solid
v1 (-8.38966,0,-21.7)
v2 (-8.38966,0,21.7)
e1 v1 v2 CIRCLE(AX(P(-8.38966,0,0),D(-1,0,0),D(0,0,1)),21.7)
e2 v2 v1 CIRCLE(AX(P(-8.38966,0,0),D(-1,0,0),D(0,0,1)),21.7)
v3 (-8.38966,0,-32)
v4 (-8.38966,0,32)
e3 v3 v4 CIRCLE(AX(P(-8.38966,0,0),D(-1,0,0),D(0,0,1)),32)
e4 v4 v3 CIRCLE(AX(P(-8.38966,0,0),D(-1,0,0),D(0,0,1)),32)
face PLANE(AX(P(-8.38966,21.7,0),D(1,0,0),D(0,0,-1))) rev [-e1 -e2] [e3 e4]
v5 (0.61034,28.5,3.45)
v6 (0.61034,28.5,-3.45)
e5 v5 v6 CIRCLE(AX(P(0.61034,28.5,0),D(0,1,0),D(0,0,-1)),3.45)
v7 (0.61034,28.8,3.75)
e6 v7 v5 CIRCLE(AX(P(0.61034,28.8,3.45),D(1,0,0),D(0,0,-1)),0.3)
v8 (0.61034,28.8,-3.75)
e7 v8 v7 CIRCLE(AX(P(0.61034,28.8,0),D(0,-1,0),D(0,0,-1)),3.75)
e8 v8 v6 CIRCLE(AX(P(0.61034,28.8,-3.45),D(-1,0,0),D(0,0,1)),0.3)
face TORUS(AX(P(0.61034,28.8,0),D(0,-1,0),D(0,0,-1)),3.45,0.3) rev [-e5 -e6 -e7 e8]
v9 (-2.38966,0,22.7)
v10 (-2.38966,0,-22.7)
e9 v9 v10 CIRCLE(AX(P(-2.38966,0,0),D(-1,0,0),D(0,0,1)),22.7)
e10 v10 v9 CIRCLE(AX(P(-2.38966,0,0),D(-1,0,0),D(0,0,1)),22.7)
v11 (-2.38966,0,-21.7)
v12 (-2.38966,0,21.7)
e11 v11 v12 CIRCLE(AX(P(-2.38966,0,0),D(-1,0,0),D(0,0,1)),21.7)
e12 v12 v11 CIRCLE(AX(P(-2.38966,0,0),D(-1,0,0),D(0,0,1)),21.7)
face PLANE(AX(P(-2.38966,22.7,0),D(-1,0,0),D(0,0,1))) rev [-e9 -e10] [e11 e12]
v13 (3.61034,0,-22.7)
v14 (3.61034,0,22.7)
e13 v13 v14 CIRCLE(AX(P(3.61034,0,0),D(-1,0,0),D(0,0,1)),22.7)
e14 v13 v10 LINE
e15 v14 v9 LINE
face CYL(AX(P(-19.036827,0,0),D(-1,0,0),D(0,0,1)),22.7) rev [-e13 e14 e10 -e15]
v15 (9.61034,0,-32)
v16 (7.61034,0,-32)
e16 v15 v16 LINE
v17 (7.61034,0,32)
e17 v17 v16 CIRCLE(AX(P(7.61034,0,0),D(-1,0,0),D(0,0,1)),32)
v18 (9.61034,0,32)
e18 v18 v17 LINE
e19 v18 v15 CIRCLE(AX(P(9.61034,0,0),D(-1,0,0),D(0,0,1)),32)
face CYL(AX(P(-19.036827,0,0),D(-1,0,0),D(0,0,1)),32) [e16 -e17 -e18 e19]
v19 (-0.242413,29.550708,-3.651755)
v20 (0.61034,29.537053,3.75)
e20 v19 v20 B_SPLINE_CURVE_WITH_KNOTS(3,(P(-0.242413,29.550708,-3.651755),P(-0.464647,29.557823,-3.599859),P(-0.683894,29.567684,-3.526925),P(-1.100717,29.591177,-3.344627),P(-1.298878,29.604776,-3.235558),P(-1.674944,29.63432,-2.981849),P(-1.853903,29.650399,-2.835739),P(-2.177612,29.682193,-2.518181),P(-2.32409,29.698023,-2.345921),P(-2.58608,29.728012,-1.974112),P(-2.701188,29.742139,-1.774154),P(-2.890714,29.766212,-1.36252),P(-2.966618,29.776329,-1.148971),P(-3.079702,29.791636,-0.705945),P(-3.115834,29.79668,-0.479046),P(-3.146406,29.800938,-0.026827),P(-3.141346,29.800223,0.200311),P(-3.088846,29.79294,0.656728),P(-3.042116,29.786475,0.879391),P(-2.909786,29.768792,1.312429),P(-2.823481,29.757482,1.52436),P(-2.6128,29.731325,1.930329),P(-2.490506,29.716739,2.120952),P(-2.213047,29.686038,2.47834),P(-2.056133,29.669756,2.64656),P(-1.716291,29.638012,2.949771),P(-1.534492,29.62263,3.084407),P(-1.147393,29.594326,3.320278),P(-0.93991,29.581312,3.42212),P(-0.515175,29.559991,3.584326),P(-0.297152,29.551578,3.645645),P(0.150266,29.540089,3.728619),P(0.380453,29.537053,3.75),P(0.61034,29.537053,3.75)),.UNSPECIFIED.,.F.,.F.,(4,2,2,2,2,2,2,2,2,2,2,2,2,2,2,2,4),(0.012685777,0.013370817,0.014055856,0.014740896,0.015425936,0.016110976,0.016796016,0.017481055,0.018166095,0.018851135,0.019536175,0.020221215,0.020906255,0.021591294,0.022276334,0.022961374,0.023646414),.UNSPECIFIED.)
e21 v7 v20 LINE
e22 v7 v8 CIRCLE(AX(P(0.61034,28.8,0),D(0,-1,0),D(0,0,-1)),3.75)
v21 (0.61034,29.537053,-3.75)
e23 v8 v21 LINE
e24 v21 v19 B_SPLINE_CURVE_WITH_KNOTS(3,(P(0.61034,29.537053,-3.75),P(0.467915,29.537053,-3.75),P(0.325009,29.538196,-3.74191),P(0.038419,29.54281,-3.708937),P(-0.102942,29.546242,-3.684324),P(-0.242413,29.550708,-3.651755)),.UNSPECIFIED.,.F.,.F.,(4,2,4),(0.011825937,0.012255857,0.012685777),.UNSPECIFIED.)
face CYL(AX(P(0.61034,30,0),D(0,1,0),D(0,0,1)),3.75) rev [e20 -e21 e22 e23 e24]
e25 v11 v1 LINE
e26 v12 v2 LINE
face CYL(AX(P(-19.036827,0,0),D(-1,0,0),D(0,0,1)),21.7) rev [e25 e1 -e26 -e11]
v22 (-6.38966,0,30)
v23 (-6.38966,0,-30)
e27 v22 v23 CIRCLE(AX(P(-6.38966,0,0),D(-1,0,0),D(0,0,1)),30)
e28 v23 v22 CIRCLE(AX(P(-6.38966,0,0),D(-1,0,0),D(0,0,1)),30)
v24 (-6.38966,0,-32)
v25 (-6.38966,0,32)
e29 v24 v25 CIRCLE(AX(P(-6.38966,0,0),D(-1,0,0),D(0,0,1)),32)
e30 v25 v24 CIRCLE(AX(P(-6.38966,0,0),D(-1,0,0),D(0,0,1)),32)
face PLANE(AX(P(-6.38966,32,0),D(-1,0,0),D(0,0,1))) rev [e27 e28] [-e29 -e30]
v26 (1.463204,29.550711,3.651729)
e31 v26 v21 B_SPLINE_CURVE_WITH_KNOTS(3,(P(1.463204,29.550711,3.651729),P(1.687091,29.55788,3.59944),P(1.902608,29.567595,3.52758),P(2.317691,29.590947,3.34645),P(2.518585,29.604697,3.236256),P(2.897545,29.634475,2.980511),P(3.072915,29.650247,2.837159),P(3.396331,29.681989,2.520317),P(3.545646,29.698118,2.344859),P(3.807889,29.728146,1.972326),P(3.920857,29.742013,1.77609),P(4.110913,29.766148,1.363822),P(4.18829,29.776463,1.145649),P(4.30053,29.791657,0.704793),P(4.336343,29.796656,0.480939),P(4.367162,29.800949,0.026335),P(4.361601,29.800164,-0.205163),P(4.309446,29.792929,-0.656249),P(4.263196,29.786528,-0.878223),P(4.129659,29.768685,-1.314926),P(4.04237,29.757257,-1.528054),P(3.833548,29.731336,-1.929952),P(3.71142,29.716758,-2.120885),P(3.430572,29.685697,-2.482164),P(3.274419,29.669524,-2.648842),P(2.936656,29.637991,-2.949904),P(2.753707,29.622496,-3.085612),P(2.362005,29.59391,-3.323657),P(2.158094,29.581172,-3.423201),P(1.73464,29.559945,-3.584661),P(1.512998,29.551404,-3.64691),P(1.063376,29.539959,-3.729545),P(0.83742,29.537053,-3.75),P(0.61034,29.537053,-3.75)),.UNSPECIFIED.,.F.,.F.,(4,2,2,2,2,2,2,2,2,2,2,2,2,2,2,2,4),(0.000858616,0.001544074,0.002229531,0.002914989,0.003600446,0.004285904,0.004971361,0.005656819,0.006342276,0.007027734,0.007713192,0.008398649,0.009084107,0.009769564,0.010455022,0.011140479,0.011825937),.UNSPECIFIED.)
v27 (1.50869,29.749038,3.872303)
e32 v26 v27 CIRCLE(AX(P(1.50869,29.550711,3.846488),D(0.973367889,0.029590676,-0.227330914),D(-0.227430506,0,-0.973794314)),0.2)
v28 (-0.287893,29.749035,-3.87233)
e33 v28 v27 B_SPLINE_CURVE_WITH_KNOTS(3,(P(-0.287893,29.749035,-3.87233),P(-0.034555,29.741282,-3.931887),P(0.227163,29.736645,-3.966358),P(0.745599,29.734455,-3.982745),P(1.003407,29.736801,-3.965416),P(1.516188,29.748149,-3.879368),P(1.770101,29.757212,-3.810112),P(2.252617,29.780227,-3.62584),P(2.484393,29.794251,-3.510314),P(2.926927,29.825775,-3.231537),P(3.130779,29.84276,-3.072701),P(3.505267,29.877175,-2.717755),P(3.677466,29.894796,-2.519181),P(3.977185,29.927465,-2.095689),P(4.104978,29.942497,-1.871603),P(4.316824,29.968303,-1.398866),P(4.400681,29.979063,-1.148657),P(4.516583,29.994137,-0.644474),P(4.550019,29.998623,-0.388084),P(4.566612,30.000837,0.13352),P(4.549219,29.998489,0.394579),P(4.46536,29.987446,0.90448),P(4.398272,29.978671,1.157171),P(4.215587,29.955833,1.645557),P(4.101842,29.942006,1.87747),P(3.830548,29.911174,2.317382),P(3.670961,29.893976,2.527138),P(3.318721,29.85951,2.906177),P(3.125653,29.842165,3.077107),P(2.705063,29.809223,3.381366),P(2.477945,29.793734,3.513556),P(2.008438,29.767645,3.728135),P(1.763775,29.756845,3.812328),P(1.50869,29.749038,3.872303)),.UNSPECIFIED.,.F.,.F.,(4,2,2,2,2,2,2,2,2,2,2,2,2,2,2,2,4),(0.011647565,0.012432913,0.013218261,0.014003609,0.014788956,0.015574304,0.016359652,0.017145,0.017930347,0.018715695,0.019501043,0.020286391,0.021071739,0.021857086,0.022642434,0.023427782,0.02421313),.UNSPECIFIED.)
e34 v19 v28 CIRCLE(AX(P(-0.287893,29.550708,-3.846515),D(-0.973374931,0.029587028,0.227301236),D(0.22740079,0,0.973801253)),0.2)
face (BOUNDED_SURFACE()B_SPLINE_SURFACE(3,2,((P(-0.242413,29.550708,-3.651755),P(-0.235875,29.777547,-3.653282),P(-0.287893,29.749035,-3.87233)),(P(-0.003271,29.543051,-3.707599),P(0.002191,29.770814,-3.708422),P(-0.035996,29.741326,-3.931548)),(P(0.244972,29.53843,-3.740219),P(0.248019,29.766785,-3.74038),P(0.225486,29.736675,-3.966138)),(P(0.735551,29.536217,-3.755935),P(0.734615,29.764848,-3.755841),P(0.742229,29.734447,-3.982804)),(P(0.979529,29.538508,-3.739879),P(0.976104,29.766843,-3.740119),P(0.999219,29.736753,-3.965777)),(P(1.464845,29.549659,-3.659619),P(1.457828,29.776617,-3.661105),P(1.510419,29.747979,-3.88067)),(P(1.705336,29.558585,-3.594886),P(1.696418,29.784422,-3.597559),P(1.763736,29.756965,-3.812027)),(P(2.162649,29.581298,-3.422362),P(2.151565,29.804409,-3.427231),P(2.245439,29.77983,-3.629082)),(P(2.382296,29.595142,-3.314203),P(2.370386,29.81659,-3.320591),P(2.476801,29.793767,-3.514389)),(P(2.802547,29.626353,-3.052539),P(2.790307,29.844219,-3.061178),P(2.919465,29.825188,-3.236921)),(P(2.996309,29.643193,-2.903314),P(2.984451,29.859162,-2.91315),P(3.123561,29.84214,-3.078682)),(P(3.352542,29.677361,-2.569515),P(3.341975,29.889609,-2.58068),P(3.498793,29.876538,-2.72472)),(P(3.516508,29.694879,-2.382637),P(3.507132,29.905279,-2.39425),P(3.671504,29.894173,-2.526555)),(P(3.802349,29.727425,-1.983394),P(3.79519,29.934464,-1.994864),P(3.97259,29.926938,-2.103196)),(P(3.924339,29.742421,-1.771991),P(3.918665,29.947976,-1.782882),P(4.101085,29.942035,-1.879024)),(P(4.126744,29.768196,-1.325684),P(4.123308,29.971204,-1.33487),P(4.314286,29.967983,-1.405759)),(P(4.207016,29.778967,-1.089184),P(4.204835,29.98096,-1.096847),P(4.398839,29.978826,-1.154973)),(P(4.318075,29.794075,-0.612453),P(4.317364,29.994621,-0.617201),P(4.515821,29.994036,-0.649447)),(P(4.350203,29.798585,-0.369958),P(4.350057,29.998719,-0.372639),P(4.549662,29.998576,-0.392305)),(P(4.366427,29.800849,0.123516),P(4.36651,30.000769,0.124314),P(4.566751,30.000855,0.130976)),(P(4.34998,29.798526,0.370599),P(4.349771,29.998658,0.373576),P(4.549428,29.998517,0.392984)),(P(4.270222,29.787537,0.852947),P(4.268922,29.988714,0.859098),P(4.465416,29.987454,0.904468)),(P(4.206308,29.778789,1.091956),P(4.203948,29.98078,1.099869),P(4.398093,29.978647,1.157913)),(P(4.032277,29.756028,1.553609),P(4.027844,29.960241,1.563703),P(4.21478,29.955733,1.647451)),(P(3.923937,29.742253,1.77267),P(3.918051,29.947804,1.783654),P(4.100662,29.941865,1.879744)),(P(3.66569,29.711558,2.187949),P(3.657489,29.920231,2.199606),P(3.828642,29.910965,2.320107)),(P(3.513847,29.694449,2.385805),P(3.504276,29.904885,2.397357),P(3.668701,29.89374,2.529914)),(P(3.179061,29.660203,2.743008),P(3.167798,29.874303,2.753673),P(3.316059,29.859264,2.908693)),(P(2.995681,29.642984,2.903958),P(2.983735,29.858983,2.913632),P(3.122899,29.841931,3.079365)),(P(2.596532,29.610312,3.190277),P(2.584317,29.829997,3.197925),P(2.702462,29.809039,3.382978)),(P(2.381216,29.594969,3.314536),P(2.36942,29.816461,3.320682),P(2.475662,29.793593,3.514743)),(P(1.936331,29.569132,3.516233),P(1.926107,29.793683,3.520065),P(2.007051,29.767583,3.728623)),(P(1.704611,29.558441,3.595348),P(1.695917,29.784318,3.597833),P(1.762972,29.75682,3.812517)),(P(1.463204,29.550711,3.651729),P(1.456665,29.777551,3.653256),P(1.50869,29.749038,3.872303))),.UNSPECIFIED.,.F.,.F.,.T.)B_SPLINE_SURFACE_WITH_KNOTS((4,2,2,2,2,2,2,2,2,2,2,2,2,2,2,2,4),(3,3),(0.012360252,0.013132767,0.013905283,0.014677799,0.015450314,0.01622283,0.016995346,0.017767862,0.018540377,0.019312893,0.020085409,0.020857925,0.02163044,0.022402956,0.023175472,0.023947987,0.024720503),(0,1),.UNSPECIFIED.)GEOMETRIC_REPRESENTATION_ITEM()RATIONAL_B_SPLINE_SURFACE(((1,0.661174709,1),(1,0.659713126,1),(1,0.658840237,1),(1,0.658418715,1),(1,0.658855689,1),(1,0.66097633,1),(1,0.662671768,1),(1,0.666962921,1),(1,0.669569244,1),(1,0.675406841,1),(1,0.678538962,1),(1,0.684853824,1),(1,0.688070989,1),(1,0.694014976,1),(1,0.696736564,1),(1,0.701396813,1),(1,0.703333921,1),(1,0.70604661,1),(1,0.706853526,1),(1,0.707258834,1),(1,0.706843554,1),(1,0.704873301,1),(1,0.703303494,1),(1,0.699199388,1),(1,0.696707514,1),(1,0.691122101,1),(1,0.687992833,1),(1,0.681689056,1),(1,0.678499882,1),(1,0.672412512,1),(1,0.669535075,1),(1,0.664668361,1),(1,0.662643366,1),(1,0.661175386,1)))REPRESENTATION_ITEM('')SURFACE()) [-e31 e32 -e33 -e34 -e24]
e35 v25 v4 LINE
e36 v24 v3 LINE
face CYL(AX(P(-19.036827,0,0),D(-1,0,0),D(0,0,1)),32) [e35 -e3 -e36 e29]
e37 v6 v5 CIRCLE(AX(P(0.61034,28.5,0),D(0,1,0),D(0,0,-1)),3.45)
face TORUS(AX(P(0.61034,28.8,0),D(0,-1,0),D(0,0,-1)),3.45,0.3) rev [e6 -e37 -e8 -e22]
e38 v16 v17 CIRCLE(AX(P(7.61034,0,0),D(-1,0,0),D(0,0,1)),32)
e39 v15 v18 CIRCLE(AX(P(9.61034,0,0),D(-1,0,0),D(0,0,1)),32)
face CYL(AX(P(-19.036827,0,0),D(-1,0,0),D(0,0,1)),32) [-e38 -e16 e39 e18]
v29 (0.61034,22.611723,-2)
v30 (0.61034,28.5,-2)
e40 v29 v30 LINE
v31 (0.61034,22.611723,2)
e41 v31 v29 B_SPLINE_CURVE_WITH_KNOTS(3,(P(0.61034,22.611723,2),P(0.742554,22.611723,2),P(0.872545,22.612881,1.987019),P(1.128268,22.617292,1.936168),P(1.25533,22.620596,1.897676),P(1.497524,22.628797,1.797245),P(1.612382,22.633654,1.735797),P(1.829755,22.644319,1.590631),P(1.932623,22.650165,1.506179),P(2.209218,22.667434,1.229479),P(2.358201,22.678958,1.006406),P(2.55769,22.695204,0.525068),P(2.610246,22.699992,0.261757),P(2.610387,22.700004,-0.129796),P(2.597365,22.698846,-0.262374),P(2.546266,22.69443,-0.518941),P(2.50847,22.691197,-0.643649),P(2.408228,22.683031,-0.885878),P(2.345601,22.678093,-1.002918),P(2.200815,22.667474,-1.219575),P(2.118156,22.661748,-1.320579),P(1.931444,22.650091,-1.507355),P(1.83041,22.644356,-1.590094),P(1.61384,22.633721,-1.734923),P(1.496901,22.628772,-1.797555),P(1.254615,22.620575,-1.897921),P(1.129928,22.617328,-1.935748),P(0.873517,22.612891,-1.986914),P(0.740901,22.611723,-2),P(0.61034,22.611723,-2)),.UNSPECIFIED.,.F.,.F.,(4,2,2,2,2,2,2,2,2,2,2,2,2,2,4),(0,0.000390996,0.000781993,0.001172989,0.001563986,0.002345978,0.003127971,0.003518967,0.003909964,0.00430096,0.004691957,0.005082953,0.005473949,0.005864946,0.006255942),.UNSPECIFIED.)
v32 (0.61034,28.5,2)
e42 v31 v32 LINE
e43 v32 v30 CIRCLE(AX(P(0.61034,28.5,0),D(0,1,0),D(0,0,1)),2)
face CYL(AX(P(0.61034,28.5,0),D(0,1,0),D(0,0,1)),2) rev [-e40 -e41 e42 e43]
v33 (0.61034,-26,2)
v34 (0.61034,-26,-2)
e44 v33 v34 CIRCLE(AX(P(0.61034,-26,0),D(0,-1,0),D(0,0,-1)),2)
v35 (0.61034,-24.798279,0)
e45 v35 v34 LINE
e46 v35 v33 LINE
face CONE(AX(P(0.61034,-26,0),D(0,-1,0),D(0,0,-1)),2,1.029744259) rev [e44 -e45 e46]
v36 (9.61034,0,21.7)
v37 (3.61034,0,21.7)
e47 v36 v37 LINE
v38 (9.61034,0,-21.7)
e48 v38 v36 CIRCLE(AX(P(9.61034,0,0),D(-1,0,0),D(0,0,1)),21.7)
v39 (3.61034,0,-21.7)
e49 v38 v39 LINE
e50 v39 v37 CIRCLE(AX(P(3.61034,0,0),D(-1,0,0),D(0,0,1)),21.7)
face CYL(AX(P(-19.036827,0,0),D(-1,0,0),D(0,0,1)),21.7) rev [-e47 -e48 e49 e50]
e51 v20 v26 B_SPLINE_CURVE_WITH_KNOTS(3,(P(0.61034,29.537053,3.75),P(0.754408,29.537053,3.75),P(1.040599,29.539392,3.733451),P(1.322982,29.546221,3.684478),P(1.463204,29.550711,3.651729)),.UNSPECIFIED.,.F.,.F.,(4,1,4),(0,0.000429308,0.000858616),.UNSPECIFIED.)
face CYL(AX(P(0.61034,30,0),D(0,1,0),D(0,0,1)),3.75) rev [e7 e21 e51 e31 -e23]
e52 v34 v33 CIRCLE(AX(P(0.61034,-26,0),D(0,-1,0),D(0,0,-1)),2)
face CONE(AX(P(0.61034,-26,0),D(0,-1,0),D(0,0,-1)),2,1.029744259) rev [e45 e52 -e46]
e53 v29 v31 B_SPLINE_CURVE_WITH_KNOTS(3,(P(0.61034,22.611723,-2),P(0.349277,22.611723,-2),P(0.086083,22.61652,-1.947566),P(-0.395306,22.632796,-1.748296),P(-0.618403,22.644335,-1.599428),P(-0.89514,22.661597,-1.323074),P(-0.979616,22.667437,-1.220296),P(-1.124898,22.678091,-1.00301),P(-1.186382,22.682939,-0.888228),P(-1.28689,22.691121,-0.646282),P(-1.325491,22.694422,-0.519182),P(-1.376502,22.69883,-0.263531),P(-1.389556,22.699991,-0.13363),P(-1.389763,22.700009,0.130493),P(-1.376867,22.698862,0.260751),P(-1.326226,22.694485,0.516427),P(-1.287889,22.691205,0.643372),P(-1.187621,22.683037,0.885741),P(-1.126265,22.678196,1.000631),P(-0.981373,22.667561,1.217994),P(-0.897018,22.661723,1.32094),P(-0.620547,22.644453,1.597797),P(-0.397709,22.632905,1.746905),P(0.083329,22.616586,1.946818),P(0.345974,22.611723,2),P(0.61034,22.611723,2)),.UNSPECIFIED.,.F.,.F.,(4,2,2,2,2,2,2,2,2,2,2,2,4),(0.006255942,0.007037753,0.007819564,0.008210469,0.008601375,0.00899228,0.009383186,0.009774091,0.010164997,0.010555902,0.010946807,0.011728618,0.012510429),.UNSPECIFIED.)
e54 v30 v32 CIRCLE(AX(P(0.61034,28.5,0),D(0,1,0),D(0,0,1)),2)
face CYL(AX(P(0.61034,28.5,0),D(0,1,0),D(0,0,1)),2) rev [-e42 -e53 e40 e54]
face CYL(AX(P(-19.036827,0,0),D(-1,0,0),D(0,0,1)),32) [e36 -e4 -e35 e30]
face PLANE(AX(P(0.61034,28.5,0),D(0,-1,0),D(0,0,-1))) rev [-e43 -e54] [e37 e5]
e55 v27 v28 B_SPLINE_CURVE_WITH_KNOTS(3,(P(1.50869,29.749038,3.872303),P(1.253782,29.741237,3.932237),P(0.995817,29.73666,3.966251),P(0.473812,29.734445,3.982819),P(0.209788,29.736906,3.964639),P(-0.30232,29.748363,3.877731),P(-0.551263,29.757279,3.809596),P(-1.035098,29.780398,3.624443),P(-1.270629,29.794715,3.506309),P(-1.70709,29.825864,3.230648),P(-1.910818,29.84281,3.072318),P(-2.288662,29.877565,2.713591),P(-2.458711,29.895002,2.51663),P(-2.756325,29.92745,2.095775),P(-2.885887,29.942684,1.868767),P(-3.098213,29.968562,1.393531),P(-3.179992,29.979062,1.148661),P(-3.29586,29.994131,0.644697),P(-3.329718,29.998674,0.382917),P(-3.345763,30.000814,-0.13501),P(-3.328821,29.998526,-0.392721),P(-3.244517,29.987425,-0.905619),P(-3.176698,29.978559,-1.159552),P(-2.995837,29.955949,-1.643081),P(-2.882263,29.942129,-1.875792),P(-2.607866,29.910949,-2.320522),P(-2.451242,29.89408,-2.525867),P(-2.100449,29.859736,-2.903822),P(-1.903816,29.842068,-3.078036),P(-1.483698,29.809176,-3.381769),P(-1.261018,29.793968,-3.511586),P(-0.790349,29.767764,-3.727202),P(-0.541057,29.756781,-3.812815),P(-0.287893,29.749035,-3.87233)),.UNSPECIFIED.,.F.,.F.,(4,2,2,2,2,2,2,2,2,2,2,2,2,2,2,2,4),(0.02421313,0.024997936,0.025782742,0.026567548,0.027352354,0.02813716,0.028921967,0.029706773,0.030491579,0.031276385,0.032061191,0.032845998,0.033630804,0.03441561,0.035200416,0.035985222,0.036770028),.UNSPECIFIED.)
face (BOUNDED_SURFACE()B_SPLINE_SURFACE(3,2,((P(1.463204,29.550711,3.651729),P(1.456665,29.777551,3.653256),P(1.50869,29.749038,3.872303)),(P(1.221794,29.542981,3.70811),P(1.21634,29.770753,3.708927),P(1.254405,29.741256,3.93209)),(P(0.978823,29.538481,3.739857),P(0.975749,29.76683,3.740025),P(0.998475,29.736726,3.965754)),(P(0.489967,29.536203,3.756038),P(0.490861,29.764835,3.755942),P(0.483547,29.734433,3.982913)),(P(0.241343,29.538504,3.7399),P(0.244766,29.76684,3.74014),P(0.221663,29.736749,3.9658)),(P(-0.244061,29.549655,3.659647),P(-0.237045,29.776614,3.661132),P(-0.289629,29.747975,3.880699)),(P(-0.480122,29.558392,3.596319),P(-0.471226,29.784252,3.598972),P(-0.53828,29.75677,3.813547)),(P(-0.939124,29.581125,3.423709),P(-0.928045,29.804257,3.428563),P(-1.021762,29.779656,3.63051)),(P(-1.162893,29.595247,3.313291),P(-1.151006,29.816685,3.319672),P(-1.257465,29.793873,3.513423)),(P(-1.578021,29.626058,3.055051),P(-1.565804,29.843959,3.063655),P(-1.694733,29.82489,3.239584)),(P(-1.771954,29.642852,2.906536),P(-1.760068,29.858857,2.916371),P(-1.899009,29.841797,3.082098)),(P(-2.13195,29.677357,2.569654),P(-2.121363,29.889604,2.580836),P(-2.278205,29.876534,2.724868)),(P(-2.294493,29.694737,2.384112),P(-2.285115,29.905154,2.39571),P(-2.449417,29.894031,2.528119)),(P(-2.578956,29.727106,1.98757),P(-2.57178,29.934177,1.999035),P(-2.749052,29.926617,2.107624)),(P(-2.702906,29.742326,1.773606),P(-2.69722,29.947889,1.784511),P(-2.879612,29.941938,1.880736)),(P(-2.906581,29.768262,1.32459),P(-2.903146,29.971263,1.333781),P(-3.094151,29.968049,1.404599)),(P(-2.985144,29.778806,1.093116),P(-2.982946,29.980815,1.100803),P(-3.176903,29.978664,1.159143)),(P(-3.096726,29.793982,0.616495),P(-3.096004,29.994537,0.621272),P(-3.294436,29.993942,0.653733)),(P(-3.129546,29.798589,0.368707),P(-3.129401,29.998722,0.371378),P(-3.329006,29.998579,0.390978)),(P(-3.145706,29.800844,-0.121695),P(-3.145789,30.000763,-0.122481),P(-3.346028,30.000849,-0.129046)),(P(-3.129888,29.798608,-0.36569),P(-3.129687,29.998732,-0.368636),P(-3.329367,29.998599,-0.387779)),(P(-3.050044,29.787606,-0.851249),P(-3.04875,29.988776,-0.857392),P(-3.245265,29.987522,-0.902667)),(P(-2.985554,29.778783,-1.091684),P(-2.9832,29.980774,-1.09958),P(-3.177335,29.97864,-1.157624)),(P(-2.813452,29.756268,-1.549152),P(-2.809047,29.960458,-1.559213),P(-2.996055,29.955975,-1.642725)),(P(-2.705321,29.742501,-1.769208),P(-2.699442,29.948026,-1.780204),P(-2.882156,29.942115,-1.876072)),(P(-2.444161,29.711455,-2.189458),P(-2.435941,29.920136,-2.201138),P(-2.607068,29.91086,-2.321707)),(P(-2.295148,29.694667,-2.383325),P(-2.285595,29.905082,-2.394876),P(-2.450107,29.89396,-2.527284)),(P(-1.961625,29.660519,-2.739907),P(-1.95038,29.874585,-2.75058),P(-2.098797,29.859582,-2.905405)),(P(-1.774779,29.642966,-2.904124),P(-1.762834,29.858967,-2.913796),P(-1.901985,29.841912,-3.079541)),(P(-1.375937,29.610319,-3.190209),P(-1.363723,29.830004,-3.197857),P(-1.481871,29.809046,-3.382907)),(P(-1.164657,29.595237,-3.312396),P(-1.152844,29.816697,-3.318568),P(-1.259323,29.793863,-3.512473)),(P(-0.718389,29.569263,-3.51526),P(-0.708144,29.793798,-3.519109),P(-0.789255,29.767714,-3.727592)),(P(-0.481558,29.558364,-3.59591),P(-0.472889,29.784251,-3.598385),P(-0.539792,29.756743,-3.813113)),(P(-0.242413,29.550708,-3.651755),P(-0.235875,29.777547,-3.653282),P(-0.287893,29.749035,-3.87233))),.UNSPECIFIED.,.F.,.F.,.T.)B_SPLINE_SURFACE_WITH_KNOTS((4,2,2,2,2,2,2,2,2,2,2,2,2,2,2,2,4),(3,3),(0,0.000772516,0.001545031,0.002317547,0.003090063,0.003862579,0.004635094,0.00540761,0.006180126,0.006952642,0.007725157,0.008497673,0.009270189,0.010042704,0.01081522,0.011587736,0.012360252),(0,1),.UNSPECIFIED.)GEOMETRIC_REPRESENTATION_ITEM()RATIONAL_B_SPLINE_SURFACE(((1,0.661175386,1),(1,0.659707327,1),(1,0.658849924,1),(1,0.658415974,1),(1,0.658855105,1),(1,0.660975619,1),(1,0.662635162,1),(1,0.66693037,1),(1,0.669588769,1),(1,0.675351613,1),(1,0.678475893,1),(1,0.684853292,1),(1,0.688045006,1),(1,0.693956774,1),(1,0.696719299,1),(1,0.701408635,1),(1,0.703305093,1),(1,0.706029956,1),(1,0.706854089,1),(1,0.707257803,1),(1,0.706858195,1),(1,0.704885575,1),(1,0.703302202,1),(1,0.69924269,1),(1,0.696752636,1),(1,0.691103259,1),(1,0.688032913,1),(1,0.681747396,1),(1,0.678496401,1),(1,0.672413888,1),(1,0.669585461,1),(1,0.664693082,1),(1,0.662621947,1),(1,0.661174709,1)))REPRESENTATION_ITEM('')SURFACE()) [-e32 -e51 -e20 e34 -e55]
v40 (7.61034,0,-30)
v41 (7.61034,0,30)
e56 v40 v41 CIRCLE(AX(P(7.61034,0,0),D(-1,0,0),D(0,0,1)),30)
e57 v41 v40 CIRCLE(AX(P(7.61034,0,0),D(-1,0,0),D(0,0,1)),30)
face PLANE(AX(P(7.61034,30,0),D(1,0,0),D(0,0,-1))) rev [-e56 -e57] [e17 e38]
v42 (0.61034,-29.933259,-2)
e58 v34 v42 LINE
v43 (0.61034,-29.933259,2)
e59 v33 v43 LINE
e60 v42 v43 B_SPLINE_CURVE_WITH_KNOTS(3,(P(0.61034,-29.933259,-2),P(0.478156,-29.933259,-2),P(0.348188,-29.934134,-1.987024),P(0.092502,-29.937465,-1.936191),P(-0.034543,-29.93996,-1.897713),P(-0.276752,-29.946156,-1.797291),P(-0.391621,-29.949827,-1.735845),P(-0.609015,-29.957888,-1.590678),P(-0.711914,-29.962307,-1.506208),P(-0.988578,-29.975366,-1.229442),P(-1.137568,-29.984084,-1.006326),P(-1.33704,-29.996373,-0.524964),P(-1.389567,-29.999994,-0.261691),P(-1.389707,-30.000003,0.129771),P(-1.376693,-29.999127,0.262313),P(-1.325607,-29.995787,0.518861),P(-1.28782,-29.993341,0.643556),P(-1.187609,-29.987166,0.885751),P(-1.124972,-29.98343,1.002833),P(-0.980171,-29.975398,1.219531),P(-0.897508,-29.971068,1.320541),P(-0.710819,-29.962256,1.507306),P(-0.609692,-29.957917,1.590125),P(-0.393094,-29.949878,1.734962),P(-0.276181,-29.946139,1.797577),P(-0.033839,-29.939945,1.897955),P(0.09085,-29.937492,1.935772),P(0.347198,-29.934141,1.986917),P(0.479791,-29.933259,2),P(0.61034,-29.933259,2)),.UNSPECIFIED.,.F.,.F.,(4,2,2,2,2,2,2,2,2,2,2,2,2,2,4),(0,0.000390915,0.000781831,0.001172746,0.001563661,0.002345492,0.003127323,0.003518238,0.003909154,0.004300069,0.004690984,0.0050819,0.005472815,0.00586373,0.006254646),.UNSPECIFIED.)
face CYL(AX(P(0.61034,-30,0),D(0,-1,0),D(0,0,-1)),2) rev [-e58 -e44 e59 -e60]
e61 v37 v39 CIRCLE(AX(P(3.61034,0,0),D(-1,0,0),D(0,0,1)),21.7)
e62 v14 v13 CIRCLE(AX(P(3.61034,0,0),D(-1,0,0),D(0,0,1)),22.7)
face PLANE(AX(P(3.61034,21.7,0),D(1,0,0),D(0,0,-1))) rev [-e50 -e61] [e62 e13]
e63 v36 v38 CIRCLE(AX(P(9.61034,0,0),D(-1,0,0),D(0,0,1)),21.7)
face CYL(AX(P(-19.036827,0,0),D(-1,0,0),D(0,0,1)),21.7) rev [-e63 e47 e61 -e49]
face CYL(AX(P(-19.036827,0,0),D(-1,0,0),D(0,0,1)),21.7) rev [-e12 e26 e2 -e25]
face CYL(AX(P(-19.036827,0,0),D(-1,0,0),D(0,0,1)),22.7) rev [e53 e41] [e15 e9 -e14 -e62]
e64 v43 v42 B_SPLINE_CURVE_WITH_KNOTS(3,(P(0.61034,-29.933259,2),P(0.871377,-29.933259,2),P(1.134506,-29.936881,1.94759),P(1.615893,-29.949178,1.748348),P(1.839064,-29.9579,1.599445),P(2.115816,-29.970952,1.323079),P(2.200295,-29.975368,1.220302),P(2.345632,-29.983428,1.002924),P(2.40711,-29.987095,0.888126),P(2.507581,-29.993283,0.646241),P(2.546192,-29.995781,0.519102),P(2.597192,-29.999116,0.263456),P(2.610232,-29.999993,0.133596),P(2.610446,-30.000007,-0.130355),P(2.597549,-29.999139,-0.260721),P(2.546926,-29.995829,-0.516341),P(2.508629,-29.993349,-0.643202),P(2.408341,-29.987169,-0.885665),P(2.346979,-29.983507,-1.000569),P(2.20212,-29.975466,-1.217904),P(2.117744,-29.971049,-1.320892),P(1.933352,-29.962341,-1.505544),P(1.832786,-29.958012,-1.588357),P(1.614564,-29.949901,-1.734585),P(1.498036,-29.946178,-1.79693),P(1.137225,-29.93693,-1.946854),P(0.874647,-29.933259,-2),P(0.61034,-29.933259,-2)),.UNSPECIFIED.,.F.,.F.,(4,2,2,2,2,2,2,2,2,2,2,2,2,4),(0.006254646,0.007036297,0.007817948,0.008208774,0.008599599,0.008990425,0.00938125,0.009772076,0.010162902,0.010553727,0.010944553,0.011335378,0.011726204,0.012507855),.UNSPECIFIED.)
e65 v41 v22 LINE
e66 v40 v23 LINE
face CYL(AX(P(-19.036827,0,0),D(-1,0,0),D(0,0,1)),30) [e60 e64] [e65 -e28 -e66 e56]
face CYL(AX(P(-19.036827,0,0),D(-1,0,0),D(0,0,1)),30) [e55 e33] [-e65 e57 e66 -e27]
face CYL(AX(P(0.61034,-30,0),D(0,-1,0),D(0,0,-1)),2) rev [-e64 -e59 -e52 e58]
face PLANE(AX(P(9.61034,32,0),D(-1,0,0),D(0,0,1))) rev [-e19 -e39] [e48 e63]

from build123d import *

# Parameters (mm, degrees)
HOLE1_D           = 7.5
HOLE1_DEPTH       = 1.5
HOLE2_REACH       = 71.113
HOLE2_BORE_R      = 2
DOWEL_HOLE1_D     = 4
DOWEL_HOLE1_DEPTH = 4
DOWEL_HOLE1_TIP   = 1.201721238
FILLET1_R         = 0.2
FILLET2_R         = 0.3


with BuildPart() as part:
    # Sketch1 → Revolve1 (revolve)
    with BuildSketch(Plane.XY, mode=Mode.PRIVATE) as revolve1_sk:
        Polygon((-8.389660143, 21.7), (-8.389660143, 32), (-6.389660143, 32), (-6.389660143, 30), (7.610339857, 30), (7.610339857, 32), (9.610339857, 32), (9.610339857, 21.7), (3.610339857, 21.7), (3.610339857, 22.7), (-2.389660143, 22.7), (-2.389660143, 21.7), align=None)
    revolve(revolve1_sk.sketch.rotate(Axis((-19.036826505, 0, 0), (1, 0, 0)), 90), axis=Axis((-19.036826505, 0, 0), (1, 0, 0)))

    # Hole1
    with Locations(Plane(origin=(0, 30, 0), x_dir=(1, 0, 0), z_dir=(0, 1, 0))):
        with Locations((0.610339857, 0)):
            Hole(HOLE1_D / 2, depth=HOLE1_DEPTH)

    # Hole2 bore → Hole2 (cut, up to next)
    with BuildSketch(Plane(origin=(0, 28.5, 0), x_dir=(1, 0, 0), z_dir=(0, 1, 0)), mode=Mode.PRIVATE) as hole2_sk1:
        with Locations((0.610339857, 0)):
            Circle(HOLE2_BORE_R)
    hole2_tool1 = extrude(hole2_sk1.sketch, amount=-HOLE2_REACH, mode=Mode.PRIVATE) & part.part
    add(hole2_tool1.solids().sort_by_distance((0.61034, 28.5, 0))[0], mode=Mode.SUBTRACT)

    # Dowel Hole1
    with Locations(Plane(origin=(0, -30, 0), x_dir=(-1, 0, 0), z_dir=(0, -1, 0))):
        with Locations((-0.610339857, 0)):
            Hole(DOWEL_HOLE1_D / 2, depth=DOWEL_HOLE1_DEPTH)
            with Locations((0, 0, -(DOWEL_HOLE1_DEPTH + DOWEL_HOLE1_TIP / 2))):  # 118° drill point
                Cone(0, DOWEL_HOLE1_D / 2, DOWEL_HOLE1_TIP, mode=Mode.SUBTRACT)

    # Fillet1
    fillet1_edges = [part.edges().sort_by_distance(p)[0] for p in [
        (4.360339864, 29.999999997, -1e-09),
    ]]
    fillet(fillet1_edges, radius=FILLET1_R)

    # Fillet2
    fillet2_edges = [part.edges().sort_by_distance(p)[0] for p in [
        (4.360339857, 28.5, 0),
    ]]
    fillet(fillet2_edges, radius=FILLET2_R)


solid = part.part
